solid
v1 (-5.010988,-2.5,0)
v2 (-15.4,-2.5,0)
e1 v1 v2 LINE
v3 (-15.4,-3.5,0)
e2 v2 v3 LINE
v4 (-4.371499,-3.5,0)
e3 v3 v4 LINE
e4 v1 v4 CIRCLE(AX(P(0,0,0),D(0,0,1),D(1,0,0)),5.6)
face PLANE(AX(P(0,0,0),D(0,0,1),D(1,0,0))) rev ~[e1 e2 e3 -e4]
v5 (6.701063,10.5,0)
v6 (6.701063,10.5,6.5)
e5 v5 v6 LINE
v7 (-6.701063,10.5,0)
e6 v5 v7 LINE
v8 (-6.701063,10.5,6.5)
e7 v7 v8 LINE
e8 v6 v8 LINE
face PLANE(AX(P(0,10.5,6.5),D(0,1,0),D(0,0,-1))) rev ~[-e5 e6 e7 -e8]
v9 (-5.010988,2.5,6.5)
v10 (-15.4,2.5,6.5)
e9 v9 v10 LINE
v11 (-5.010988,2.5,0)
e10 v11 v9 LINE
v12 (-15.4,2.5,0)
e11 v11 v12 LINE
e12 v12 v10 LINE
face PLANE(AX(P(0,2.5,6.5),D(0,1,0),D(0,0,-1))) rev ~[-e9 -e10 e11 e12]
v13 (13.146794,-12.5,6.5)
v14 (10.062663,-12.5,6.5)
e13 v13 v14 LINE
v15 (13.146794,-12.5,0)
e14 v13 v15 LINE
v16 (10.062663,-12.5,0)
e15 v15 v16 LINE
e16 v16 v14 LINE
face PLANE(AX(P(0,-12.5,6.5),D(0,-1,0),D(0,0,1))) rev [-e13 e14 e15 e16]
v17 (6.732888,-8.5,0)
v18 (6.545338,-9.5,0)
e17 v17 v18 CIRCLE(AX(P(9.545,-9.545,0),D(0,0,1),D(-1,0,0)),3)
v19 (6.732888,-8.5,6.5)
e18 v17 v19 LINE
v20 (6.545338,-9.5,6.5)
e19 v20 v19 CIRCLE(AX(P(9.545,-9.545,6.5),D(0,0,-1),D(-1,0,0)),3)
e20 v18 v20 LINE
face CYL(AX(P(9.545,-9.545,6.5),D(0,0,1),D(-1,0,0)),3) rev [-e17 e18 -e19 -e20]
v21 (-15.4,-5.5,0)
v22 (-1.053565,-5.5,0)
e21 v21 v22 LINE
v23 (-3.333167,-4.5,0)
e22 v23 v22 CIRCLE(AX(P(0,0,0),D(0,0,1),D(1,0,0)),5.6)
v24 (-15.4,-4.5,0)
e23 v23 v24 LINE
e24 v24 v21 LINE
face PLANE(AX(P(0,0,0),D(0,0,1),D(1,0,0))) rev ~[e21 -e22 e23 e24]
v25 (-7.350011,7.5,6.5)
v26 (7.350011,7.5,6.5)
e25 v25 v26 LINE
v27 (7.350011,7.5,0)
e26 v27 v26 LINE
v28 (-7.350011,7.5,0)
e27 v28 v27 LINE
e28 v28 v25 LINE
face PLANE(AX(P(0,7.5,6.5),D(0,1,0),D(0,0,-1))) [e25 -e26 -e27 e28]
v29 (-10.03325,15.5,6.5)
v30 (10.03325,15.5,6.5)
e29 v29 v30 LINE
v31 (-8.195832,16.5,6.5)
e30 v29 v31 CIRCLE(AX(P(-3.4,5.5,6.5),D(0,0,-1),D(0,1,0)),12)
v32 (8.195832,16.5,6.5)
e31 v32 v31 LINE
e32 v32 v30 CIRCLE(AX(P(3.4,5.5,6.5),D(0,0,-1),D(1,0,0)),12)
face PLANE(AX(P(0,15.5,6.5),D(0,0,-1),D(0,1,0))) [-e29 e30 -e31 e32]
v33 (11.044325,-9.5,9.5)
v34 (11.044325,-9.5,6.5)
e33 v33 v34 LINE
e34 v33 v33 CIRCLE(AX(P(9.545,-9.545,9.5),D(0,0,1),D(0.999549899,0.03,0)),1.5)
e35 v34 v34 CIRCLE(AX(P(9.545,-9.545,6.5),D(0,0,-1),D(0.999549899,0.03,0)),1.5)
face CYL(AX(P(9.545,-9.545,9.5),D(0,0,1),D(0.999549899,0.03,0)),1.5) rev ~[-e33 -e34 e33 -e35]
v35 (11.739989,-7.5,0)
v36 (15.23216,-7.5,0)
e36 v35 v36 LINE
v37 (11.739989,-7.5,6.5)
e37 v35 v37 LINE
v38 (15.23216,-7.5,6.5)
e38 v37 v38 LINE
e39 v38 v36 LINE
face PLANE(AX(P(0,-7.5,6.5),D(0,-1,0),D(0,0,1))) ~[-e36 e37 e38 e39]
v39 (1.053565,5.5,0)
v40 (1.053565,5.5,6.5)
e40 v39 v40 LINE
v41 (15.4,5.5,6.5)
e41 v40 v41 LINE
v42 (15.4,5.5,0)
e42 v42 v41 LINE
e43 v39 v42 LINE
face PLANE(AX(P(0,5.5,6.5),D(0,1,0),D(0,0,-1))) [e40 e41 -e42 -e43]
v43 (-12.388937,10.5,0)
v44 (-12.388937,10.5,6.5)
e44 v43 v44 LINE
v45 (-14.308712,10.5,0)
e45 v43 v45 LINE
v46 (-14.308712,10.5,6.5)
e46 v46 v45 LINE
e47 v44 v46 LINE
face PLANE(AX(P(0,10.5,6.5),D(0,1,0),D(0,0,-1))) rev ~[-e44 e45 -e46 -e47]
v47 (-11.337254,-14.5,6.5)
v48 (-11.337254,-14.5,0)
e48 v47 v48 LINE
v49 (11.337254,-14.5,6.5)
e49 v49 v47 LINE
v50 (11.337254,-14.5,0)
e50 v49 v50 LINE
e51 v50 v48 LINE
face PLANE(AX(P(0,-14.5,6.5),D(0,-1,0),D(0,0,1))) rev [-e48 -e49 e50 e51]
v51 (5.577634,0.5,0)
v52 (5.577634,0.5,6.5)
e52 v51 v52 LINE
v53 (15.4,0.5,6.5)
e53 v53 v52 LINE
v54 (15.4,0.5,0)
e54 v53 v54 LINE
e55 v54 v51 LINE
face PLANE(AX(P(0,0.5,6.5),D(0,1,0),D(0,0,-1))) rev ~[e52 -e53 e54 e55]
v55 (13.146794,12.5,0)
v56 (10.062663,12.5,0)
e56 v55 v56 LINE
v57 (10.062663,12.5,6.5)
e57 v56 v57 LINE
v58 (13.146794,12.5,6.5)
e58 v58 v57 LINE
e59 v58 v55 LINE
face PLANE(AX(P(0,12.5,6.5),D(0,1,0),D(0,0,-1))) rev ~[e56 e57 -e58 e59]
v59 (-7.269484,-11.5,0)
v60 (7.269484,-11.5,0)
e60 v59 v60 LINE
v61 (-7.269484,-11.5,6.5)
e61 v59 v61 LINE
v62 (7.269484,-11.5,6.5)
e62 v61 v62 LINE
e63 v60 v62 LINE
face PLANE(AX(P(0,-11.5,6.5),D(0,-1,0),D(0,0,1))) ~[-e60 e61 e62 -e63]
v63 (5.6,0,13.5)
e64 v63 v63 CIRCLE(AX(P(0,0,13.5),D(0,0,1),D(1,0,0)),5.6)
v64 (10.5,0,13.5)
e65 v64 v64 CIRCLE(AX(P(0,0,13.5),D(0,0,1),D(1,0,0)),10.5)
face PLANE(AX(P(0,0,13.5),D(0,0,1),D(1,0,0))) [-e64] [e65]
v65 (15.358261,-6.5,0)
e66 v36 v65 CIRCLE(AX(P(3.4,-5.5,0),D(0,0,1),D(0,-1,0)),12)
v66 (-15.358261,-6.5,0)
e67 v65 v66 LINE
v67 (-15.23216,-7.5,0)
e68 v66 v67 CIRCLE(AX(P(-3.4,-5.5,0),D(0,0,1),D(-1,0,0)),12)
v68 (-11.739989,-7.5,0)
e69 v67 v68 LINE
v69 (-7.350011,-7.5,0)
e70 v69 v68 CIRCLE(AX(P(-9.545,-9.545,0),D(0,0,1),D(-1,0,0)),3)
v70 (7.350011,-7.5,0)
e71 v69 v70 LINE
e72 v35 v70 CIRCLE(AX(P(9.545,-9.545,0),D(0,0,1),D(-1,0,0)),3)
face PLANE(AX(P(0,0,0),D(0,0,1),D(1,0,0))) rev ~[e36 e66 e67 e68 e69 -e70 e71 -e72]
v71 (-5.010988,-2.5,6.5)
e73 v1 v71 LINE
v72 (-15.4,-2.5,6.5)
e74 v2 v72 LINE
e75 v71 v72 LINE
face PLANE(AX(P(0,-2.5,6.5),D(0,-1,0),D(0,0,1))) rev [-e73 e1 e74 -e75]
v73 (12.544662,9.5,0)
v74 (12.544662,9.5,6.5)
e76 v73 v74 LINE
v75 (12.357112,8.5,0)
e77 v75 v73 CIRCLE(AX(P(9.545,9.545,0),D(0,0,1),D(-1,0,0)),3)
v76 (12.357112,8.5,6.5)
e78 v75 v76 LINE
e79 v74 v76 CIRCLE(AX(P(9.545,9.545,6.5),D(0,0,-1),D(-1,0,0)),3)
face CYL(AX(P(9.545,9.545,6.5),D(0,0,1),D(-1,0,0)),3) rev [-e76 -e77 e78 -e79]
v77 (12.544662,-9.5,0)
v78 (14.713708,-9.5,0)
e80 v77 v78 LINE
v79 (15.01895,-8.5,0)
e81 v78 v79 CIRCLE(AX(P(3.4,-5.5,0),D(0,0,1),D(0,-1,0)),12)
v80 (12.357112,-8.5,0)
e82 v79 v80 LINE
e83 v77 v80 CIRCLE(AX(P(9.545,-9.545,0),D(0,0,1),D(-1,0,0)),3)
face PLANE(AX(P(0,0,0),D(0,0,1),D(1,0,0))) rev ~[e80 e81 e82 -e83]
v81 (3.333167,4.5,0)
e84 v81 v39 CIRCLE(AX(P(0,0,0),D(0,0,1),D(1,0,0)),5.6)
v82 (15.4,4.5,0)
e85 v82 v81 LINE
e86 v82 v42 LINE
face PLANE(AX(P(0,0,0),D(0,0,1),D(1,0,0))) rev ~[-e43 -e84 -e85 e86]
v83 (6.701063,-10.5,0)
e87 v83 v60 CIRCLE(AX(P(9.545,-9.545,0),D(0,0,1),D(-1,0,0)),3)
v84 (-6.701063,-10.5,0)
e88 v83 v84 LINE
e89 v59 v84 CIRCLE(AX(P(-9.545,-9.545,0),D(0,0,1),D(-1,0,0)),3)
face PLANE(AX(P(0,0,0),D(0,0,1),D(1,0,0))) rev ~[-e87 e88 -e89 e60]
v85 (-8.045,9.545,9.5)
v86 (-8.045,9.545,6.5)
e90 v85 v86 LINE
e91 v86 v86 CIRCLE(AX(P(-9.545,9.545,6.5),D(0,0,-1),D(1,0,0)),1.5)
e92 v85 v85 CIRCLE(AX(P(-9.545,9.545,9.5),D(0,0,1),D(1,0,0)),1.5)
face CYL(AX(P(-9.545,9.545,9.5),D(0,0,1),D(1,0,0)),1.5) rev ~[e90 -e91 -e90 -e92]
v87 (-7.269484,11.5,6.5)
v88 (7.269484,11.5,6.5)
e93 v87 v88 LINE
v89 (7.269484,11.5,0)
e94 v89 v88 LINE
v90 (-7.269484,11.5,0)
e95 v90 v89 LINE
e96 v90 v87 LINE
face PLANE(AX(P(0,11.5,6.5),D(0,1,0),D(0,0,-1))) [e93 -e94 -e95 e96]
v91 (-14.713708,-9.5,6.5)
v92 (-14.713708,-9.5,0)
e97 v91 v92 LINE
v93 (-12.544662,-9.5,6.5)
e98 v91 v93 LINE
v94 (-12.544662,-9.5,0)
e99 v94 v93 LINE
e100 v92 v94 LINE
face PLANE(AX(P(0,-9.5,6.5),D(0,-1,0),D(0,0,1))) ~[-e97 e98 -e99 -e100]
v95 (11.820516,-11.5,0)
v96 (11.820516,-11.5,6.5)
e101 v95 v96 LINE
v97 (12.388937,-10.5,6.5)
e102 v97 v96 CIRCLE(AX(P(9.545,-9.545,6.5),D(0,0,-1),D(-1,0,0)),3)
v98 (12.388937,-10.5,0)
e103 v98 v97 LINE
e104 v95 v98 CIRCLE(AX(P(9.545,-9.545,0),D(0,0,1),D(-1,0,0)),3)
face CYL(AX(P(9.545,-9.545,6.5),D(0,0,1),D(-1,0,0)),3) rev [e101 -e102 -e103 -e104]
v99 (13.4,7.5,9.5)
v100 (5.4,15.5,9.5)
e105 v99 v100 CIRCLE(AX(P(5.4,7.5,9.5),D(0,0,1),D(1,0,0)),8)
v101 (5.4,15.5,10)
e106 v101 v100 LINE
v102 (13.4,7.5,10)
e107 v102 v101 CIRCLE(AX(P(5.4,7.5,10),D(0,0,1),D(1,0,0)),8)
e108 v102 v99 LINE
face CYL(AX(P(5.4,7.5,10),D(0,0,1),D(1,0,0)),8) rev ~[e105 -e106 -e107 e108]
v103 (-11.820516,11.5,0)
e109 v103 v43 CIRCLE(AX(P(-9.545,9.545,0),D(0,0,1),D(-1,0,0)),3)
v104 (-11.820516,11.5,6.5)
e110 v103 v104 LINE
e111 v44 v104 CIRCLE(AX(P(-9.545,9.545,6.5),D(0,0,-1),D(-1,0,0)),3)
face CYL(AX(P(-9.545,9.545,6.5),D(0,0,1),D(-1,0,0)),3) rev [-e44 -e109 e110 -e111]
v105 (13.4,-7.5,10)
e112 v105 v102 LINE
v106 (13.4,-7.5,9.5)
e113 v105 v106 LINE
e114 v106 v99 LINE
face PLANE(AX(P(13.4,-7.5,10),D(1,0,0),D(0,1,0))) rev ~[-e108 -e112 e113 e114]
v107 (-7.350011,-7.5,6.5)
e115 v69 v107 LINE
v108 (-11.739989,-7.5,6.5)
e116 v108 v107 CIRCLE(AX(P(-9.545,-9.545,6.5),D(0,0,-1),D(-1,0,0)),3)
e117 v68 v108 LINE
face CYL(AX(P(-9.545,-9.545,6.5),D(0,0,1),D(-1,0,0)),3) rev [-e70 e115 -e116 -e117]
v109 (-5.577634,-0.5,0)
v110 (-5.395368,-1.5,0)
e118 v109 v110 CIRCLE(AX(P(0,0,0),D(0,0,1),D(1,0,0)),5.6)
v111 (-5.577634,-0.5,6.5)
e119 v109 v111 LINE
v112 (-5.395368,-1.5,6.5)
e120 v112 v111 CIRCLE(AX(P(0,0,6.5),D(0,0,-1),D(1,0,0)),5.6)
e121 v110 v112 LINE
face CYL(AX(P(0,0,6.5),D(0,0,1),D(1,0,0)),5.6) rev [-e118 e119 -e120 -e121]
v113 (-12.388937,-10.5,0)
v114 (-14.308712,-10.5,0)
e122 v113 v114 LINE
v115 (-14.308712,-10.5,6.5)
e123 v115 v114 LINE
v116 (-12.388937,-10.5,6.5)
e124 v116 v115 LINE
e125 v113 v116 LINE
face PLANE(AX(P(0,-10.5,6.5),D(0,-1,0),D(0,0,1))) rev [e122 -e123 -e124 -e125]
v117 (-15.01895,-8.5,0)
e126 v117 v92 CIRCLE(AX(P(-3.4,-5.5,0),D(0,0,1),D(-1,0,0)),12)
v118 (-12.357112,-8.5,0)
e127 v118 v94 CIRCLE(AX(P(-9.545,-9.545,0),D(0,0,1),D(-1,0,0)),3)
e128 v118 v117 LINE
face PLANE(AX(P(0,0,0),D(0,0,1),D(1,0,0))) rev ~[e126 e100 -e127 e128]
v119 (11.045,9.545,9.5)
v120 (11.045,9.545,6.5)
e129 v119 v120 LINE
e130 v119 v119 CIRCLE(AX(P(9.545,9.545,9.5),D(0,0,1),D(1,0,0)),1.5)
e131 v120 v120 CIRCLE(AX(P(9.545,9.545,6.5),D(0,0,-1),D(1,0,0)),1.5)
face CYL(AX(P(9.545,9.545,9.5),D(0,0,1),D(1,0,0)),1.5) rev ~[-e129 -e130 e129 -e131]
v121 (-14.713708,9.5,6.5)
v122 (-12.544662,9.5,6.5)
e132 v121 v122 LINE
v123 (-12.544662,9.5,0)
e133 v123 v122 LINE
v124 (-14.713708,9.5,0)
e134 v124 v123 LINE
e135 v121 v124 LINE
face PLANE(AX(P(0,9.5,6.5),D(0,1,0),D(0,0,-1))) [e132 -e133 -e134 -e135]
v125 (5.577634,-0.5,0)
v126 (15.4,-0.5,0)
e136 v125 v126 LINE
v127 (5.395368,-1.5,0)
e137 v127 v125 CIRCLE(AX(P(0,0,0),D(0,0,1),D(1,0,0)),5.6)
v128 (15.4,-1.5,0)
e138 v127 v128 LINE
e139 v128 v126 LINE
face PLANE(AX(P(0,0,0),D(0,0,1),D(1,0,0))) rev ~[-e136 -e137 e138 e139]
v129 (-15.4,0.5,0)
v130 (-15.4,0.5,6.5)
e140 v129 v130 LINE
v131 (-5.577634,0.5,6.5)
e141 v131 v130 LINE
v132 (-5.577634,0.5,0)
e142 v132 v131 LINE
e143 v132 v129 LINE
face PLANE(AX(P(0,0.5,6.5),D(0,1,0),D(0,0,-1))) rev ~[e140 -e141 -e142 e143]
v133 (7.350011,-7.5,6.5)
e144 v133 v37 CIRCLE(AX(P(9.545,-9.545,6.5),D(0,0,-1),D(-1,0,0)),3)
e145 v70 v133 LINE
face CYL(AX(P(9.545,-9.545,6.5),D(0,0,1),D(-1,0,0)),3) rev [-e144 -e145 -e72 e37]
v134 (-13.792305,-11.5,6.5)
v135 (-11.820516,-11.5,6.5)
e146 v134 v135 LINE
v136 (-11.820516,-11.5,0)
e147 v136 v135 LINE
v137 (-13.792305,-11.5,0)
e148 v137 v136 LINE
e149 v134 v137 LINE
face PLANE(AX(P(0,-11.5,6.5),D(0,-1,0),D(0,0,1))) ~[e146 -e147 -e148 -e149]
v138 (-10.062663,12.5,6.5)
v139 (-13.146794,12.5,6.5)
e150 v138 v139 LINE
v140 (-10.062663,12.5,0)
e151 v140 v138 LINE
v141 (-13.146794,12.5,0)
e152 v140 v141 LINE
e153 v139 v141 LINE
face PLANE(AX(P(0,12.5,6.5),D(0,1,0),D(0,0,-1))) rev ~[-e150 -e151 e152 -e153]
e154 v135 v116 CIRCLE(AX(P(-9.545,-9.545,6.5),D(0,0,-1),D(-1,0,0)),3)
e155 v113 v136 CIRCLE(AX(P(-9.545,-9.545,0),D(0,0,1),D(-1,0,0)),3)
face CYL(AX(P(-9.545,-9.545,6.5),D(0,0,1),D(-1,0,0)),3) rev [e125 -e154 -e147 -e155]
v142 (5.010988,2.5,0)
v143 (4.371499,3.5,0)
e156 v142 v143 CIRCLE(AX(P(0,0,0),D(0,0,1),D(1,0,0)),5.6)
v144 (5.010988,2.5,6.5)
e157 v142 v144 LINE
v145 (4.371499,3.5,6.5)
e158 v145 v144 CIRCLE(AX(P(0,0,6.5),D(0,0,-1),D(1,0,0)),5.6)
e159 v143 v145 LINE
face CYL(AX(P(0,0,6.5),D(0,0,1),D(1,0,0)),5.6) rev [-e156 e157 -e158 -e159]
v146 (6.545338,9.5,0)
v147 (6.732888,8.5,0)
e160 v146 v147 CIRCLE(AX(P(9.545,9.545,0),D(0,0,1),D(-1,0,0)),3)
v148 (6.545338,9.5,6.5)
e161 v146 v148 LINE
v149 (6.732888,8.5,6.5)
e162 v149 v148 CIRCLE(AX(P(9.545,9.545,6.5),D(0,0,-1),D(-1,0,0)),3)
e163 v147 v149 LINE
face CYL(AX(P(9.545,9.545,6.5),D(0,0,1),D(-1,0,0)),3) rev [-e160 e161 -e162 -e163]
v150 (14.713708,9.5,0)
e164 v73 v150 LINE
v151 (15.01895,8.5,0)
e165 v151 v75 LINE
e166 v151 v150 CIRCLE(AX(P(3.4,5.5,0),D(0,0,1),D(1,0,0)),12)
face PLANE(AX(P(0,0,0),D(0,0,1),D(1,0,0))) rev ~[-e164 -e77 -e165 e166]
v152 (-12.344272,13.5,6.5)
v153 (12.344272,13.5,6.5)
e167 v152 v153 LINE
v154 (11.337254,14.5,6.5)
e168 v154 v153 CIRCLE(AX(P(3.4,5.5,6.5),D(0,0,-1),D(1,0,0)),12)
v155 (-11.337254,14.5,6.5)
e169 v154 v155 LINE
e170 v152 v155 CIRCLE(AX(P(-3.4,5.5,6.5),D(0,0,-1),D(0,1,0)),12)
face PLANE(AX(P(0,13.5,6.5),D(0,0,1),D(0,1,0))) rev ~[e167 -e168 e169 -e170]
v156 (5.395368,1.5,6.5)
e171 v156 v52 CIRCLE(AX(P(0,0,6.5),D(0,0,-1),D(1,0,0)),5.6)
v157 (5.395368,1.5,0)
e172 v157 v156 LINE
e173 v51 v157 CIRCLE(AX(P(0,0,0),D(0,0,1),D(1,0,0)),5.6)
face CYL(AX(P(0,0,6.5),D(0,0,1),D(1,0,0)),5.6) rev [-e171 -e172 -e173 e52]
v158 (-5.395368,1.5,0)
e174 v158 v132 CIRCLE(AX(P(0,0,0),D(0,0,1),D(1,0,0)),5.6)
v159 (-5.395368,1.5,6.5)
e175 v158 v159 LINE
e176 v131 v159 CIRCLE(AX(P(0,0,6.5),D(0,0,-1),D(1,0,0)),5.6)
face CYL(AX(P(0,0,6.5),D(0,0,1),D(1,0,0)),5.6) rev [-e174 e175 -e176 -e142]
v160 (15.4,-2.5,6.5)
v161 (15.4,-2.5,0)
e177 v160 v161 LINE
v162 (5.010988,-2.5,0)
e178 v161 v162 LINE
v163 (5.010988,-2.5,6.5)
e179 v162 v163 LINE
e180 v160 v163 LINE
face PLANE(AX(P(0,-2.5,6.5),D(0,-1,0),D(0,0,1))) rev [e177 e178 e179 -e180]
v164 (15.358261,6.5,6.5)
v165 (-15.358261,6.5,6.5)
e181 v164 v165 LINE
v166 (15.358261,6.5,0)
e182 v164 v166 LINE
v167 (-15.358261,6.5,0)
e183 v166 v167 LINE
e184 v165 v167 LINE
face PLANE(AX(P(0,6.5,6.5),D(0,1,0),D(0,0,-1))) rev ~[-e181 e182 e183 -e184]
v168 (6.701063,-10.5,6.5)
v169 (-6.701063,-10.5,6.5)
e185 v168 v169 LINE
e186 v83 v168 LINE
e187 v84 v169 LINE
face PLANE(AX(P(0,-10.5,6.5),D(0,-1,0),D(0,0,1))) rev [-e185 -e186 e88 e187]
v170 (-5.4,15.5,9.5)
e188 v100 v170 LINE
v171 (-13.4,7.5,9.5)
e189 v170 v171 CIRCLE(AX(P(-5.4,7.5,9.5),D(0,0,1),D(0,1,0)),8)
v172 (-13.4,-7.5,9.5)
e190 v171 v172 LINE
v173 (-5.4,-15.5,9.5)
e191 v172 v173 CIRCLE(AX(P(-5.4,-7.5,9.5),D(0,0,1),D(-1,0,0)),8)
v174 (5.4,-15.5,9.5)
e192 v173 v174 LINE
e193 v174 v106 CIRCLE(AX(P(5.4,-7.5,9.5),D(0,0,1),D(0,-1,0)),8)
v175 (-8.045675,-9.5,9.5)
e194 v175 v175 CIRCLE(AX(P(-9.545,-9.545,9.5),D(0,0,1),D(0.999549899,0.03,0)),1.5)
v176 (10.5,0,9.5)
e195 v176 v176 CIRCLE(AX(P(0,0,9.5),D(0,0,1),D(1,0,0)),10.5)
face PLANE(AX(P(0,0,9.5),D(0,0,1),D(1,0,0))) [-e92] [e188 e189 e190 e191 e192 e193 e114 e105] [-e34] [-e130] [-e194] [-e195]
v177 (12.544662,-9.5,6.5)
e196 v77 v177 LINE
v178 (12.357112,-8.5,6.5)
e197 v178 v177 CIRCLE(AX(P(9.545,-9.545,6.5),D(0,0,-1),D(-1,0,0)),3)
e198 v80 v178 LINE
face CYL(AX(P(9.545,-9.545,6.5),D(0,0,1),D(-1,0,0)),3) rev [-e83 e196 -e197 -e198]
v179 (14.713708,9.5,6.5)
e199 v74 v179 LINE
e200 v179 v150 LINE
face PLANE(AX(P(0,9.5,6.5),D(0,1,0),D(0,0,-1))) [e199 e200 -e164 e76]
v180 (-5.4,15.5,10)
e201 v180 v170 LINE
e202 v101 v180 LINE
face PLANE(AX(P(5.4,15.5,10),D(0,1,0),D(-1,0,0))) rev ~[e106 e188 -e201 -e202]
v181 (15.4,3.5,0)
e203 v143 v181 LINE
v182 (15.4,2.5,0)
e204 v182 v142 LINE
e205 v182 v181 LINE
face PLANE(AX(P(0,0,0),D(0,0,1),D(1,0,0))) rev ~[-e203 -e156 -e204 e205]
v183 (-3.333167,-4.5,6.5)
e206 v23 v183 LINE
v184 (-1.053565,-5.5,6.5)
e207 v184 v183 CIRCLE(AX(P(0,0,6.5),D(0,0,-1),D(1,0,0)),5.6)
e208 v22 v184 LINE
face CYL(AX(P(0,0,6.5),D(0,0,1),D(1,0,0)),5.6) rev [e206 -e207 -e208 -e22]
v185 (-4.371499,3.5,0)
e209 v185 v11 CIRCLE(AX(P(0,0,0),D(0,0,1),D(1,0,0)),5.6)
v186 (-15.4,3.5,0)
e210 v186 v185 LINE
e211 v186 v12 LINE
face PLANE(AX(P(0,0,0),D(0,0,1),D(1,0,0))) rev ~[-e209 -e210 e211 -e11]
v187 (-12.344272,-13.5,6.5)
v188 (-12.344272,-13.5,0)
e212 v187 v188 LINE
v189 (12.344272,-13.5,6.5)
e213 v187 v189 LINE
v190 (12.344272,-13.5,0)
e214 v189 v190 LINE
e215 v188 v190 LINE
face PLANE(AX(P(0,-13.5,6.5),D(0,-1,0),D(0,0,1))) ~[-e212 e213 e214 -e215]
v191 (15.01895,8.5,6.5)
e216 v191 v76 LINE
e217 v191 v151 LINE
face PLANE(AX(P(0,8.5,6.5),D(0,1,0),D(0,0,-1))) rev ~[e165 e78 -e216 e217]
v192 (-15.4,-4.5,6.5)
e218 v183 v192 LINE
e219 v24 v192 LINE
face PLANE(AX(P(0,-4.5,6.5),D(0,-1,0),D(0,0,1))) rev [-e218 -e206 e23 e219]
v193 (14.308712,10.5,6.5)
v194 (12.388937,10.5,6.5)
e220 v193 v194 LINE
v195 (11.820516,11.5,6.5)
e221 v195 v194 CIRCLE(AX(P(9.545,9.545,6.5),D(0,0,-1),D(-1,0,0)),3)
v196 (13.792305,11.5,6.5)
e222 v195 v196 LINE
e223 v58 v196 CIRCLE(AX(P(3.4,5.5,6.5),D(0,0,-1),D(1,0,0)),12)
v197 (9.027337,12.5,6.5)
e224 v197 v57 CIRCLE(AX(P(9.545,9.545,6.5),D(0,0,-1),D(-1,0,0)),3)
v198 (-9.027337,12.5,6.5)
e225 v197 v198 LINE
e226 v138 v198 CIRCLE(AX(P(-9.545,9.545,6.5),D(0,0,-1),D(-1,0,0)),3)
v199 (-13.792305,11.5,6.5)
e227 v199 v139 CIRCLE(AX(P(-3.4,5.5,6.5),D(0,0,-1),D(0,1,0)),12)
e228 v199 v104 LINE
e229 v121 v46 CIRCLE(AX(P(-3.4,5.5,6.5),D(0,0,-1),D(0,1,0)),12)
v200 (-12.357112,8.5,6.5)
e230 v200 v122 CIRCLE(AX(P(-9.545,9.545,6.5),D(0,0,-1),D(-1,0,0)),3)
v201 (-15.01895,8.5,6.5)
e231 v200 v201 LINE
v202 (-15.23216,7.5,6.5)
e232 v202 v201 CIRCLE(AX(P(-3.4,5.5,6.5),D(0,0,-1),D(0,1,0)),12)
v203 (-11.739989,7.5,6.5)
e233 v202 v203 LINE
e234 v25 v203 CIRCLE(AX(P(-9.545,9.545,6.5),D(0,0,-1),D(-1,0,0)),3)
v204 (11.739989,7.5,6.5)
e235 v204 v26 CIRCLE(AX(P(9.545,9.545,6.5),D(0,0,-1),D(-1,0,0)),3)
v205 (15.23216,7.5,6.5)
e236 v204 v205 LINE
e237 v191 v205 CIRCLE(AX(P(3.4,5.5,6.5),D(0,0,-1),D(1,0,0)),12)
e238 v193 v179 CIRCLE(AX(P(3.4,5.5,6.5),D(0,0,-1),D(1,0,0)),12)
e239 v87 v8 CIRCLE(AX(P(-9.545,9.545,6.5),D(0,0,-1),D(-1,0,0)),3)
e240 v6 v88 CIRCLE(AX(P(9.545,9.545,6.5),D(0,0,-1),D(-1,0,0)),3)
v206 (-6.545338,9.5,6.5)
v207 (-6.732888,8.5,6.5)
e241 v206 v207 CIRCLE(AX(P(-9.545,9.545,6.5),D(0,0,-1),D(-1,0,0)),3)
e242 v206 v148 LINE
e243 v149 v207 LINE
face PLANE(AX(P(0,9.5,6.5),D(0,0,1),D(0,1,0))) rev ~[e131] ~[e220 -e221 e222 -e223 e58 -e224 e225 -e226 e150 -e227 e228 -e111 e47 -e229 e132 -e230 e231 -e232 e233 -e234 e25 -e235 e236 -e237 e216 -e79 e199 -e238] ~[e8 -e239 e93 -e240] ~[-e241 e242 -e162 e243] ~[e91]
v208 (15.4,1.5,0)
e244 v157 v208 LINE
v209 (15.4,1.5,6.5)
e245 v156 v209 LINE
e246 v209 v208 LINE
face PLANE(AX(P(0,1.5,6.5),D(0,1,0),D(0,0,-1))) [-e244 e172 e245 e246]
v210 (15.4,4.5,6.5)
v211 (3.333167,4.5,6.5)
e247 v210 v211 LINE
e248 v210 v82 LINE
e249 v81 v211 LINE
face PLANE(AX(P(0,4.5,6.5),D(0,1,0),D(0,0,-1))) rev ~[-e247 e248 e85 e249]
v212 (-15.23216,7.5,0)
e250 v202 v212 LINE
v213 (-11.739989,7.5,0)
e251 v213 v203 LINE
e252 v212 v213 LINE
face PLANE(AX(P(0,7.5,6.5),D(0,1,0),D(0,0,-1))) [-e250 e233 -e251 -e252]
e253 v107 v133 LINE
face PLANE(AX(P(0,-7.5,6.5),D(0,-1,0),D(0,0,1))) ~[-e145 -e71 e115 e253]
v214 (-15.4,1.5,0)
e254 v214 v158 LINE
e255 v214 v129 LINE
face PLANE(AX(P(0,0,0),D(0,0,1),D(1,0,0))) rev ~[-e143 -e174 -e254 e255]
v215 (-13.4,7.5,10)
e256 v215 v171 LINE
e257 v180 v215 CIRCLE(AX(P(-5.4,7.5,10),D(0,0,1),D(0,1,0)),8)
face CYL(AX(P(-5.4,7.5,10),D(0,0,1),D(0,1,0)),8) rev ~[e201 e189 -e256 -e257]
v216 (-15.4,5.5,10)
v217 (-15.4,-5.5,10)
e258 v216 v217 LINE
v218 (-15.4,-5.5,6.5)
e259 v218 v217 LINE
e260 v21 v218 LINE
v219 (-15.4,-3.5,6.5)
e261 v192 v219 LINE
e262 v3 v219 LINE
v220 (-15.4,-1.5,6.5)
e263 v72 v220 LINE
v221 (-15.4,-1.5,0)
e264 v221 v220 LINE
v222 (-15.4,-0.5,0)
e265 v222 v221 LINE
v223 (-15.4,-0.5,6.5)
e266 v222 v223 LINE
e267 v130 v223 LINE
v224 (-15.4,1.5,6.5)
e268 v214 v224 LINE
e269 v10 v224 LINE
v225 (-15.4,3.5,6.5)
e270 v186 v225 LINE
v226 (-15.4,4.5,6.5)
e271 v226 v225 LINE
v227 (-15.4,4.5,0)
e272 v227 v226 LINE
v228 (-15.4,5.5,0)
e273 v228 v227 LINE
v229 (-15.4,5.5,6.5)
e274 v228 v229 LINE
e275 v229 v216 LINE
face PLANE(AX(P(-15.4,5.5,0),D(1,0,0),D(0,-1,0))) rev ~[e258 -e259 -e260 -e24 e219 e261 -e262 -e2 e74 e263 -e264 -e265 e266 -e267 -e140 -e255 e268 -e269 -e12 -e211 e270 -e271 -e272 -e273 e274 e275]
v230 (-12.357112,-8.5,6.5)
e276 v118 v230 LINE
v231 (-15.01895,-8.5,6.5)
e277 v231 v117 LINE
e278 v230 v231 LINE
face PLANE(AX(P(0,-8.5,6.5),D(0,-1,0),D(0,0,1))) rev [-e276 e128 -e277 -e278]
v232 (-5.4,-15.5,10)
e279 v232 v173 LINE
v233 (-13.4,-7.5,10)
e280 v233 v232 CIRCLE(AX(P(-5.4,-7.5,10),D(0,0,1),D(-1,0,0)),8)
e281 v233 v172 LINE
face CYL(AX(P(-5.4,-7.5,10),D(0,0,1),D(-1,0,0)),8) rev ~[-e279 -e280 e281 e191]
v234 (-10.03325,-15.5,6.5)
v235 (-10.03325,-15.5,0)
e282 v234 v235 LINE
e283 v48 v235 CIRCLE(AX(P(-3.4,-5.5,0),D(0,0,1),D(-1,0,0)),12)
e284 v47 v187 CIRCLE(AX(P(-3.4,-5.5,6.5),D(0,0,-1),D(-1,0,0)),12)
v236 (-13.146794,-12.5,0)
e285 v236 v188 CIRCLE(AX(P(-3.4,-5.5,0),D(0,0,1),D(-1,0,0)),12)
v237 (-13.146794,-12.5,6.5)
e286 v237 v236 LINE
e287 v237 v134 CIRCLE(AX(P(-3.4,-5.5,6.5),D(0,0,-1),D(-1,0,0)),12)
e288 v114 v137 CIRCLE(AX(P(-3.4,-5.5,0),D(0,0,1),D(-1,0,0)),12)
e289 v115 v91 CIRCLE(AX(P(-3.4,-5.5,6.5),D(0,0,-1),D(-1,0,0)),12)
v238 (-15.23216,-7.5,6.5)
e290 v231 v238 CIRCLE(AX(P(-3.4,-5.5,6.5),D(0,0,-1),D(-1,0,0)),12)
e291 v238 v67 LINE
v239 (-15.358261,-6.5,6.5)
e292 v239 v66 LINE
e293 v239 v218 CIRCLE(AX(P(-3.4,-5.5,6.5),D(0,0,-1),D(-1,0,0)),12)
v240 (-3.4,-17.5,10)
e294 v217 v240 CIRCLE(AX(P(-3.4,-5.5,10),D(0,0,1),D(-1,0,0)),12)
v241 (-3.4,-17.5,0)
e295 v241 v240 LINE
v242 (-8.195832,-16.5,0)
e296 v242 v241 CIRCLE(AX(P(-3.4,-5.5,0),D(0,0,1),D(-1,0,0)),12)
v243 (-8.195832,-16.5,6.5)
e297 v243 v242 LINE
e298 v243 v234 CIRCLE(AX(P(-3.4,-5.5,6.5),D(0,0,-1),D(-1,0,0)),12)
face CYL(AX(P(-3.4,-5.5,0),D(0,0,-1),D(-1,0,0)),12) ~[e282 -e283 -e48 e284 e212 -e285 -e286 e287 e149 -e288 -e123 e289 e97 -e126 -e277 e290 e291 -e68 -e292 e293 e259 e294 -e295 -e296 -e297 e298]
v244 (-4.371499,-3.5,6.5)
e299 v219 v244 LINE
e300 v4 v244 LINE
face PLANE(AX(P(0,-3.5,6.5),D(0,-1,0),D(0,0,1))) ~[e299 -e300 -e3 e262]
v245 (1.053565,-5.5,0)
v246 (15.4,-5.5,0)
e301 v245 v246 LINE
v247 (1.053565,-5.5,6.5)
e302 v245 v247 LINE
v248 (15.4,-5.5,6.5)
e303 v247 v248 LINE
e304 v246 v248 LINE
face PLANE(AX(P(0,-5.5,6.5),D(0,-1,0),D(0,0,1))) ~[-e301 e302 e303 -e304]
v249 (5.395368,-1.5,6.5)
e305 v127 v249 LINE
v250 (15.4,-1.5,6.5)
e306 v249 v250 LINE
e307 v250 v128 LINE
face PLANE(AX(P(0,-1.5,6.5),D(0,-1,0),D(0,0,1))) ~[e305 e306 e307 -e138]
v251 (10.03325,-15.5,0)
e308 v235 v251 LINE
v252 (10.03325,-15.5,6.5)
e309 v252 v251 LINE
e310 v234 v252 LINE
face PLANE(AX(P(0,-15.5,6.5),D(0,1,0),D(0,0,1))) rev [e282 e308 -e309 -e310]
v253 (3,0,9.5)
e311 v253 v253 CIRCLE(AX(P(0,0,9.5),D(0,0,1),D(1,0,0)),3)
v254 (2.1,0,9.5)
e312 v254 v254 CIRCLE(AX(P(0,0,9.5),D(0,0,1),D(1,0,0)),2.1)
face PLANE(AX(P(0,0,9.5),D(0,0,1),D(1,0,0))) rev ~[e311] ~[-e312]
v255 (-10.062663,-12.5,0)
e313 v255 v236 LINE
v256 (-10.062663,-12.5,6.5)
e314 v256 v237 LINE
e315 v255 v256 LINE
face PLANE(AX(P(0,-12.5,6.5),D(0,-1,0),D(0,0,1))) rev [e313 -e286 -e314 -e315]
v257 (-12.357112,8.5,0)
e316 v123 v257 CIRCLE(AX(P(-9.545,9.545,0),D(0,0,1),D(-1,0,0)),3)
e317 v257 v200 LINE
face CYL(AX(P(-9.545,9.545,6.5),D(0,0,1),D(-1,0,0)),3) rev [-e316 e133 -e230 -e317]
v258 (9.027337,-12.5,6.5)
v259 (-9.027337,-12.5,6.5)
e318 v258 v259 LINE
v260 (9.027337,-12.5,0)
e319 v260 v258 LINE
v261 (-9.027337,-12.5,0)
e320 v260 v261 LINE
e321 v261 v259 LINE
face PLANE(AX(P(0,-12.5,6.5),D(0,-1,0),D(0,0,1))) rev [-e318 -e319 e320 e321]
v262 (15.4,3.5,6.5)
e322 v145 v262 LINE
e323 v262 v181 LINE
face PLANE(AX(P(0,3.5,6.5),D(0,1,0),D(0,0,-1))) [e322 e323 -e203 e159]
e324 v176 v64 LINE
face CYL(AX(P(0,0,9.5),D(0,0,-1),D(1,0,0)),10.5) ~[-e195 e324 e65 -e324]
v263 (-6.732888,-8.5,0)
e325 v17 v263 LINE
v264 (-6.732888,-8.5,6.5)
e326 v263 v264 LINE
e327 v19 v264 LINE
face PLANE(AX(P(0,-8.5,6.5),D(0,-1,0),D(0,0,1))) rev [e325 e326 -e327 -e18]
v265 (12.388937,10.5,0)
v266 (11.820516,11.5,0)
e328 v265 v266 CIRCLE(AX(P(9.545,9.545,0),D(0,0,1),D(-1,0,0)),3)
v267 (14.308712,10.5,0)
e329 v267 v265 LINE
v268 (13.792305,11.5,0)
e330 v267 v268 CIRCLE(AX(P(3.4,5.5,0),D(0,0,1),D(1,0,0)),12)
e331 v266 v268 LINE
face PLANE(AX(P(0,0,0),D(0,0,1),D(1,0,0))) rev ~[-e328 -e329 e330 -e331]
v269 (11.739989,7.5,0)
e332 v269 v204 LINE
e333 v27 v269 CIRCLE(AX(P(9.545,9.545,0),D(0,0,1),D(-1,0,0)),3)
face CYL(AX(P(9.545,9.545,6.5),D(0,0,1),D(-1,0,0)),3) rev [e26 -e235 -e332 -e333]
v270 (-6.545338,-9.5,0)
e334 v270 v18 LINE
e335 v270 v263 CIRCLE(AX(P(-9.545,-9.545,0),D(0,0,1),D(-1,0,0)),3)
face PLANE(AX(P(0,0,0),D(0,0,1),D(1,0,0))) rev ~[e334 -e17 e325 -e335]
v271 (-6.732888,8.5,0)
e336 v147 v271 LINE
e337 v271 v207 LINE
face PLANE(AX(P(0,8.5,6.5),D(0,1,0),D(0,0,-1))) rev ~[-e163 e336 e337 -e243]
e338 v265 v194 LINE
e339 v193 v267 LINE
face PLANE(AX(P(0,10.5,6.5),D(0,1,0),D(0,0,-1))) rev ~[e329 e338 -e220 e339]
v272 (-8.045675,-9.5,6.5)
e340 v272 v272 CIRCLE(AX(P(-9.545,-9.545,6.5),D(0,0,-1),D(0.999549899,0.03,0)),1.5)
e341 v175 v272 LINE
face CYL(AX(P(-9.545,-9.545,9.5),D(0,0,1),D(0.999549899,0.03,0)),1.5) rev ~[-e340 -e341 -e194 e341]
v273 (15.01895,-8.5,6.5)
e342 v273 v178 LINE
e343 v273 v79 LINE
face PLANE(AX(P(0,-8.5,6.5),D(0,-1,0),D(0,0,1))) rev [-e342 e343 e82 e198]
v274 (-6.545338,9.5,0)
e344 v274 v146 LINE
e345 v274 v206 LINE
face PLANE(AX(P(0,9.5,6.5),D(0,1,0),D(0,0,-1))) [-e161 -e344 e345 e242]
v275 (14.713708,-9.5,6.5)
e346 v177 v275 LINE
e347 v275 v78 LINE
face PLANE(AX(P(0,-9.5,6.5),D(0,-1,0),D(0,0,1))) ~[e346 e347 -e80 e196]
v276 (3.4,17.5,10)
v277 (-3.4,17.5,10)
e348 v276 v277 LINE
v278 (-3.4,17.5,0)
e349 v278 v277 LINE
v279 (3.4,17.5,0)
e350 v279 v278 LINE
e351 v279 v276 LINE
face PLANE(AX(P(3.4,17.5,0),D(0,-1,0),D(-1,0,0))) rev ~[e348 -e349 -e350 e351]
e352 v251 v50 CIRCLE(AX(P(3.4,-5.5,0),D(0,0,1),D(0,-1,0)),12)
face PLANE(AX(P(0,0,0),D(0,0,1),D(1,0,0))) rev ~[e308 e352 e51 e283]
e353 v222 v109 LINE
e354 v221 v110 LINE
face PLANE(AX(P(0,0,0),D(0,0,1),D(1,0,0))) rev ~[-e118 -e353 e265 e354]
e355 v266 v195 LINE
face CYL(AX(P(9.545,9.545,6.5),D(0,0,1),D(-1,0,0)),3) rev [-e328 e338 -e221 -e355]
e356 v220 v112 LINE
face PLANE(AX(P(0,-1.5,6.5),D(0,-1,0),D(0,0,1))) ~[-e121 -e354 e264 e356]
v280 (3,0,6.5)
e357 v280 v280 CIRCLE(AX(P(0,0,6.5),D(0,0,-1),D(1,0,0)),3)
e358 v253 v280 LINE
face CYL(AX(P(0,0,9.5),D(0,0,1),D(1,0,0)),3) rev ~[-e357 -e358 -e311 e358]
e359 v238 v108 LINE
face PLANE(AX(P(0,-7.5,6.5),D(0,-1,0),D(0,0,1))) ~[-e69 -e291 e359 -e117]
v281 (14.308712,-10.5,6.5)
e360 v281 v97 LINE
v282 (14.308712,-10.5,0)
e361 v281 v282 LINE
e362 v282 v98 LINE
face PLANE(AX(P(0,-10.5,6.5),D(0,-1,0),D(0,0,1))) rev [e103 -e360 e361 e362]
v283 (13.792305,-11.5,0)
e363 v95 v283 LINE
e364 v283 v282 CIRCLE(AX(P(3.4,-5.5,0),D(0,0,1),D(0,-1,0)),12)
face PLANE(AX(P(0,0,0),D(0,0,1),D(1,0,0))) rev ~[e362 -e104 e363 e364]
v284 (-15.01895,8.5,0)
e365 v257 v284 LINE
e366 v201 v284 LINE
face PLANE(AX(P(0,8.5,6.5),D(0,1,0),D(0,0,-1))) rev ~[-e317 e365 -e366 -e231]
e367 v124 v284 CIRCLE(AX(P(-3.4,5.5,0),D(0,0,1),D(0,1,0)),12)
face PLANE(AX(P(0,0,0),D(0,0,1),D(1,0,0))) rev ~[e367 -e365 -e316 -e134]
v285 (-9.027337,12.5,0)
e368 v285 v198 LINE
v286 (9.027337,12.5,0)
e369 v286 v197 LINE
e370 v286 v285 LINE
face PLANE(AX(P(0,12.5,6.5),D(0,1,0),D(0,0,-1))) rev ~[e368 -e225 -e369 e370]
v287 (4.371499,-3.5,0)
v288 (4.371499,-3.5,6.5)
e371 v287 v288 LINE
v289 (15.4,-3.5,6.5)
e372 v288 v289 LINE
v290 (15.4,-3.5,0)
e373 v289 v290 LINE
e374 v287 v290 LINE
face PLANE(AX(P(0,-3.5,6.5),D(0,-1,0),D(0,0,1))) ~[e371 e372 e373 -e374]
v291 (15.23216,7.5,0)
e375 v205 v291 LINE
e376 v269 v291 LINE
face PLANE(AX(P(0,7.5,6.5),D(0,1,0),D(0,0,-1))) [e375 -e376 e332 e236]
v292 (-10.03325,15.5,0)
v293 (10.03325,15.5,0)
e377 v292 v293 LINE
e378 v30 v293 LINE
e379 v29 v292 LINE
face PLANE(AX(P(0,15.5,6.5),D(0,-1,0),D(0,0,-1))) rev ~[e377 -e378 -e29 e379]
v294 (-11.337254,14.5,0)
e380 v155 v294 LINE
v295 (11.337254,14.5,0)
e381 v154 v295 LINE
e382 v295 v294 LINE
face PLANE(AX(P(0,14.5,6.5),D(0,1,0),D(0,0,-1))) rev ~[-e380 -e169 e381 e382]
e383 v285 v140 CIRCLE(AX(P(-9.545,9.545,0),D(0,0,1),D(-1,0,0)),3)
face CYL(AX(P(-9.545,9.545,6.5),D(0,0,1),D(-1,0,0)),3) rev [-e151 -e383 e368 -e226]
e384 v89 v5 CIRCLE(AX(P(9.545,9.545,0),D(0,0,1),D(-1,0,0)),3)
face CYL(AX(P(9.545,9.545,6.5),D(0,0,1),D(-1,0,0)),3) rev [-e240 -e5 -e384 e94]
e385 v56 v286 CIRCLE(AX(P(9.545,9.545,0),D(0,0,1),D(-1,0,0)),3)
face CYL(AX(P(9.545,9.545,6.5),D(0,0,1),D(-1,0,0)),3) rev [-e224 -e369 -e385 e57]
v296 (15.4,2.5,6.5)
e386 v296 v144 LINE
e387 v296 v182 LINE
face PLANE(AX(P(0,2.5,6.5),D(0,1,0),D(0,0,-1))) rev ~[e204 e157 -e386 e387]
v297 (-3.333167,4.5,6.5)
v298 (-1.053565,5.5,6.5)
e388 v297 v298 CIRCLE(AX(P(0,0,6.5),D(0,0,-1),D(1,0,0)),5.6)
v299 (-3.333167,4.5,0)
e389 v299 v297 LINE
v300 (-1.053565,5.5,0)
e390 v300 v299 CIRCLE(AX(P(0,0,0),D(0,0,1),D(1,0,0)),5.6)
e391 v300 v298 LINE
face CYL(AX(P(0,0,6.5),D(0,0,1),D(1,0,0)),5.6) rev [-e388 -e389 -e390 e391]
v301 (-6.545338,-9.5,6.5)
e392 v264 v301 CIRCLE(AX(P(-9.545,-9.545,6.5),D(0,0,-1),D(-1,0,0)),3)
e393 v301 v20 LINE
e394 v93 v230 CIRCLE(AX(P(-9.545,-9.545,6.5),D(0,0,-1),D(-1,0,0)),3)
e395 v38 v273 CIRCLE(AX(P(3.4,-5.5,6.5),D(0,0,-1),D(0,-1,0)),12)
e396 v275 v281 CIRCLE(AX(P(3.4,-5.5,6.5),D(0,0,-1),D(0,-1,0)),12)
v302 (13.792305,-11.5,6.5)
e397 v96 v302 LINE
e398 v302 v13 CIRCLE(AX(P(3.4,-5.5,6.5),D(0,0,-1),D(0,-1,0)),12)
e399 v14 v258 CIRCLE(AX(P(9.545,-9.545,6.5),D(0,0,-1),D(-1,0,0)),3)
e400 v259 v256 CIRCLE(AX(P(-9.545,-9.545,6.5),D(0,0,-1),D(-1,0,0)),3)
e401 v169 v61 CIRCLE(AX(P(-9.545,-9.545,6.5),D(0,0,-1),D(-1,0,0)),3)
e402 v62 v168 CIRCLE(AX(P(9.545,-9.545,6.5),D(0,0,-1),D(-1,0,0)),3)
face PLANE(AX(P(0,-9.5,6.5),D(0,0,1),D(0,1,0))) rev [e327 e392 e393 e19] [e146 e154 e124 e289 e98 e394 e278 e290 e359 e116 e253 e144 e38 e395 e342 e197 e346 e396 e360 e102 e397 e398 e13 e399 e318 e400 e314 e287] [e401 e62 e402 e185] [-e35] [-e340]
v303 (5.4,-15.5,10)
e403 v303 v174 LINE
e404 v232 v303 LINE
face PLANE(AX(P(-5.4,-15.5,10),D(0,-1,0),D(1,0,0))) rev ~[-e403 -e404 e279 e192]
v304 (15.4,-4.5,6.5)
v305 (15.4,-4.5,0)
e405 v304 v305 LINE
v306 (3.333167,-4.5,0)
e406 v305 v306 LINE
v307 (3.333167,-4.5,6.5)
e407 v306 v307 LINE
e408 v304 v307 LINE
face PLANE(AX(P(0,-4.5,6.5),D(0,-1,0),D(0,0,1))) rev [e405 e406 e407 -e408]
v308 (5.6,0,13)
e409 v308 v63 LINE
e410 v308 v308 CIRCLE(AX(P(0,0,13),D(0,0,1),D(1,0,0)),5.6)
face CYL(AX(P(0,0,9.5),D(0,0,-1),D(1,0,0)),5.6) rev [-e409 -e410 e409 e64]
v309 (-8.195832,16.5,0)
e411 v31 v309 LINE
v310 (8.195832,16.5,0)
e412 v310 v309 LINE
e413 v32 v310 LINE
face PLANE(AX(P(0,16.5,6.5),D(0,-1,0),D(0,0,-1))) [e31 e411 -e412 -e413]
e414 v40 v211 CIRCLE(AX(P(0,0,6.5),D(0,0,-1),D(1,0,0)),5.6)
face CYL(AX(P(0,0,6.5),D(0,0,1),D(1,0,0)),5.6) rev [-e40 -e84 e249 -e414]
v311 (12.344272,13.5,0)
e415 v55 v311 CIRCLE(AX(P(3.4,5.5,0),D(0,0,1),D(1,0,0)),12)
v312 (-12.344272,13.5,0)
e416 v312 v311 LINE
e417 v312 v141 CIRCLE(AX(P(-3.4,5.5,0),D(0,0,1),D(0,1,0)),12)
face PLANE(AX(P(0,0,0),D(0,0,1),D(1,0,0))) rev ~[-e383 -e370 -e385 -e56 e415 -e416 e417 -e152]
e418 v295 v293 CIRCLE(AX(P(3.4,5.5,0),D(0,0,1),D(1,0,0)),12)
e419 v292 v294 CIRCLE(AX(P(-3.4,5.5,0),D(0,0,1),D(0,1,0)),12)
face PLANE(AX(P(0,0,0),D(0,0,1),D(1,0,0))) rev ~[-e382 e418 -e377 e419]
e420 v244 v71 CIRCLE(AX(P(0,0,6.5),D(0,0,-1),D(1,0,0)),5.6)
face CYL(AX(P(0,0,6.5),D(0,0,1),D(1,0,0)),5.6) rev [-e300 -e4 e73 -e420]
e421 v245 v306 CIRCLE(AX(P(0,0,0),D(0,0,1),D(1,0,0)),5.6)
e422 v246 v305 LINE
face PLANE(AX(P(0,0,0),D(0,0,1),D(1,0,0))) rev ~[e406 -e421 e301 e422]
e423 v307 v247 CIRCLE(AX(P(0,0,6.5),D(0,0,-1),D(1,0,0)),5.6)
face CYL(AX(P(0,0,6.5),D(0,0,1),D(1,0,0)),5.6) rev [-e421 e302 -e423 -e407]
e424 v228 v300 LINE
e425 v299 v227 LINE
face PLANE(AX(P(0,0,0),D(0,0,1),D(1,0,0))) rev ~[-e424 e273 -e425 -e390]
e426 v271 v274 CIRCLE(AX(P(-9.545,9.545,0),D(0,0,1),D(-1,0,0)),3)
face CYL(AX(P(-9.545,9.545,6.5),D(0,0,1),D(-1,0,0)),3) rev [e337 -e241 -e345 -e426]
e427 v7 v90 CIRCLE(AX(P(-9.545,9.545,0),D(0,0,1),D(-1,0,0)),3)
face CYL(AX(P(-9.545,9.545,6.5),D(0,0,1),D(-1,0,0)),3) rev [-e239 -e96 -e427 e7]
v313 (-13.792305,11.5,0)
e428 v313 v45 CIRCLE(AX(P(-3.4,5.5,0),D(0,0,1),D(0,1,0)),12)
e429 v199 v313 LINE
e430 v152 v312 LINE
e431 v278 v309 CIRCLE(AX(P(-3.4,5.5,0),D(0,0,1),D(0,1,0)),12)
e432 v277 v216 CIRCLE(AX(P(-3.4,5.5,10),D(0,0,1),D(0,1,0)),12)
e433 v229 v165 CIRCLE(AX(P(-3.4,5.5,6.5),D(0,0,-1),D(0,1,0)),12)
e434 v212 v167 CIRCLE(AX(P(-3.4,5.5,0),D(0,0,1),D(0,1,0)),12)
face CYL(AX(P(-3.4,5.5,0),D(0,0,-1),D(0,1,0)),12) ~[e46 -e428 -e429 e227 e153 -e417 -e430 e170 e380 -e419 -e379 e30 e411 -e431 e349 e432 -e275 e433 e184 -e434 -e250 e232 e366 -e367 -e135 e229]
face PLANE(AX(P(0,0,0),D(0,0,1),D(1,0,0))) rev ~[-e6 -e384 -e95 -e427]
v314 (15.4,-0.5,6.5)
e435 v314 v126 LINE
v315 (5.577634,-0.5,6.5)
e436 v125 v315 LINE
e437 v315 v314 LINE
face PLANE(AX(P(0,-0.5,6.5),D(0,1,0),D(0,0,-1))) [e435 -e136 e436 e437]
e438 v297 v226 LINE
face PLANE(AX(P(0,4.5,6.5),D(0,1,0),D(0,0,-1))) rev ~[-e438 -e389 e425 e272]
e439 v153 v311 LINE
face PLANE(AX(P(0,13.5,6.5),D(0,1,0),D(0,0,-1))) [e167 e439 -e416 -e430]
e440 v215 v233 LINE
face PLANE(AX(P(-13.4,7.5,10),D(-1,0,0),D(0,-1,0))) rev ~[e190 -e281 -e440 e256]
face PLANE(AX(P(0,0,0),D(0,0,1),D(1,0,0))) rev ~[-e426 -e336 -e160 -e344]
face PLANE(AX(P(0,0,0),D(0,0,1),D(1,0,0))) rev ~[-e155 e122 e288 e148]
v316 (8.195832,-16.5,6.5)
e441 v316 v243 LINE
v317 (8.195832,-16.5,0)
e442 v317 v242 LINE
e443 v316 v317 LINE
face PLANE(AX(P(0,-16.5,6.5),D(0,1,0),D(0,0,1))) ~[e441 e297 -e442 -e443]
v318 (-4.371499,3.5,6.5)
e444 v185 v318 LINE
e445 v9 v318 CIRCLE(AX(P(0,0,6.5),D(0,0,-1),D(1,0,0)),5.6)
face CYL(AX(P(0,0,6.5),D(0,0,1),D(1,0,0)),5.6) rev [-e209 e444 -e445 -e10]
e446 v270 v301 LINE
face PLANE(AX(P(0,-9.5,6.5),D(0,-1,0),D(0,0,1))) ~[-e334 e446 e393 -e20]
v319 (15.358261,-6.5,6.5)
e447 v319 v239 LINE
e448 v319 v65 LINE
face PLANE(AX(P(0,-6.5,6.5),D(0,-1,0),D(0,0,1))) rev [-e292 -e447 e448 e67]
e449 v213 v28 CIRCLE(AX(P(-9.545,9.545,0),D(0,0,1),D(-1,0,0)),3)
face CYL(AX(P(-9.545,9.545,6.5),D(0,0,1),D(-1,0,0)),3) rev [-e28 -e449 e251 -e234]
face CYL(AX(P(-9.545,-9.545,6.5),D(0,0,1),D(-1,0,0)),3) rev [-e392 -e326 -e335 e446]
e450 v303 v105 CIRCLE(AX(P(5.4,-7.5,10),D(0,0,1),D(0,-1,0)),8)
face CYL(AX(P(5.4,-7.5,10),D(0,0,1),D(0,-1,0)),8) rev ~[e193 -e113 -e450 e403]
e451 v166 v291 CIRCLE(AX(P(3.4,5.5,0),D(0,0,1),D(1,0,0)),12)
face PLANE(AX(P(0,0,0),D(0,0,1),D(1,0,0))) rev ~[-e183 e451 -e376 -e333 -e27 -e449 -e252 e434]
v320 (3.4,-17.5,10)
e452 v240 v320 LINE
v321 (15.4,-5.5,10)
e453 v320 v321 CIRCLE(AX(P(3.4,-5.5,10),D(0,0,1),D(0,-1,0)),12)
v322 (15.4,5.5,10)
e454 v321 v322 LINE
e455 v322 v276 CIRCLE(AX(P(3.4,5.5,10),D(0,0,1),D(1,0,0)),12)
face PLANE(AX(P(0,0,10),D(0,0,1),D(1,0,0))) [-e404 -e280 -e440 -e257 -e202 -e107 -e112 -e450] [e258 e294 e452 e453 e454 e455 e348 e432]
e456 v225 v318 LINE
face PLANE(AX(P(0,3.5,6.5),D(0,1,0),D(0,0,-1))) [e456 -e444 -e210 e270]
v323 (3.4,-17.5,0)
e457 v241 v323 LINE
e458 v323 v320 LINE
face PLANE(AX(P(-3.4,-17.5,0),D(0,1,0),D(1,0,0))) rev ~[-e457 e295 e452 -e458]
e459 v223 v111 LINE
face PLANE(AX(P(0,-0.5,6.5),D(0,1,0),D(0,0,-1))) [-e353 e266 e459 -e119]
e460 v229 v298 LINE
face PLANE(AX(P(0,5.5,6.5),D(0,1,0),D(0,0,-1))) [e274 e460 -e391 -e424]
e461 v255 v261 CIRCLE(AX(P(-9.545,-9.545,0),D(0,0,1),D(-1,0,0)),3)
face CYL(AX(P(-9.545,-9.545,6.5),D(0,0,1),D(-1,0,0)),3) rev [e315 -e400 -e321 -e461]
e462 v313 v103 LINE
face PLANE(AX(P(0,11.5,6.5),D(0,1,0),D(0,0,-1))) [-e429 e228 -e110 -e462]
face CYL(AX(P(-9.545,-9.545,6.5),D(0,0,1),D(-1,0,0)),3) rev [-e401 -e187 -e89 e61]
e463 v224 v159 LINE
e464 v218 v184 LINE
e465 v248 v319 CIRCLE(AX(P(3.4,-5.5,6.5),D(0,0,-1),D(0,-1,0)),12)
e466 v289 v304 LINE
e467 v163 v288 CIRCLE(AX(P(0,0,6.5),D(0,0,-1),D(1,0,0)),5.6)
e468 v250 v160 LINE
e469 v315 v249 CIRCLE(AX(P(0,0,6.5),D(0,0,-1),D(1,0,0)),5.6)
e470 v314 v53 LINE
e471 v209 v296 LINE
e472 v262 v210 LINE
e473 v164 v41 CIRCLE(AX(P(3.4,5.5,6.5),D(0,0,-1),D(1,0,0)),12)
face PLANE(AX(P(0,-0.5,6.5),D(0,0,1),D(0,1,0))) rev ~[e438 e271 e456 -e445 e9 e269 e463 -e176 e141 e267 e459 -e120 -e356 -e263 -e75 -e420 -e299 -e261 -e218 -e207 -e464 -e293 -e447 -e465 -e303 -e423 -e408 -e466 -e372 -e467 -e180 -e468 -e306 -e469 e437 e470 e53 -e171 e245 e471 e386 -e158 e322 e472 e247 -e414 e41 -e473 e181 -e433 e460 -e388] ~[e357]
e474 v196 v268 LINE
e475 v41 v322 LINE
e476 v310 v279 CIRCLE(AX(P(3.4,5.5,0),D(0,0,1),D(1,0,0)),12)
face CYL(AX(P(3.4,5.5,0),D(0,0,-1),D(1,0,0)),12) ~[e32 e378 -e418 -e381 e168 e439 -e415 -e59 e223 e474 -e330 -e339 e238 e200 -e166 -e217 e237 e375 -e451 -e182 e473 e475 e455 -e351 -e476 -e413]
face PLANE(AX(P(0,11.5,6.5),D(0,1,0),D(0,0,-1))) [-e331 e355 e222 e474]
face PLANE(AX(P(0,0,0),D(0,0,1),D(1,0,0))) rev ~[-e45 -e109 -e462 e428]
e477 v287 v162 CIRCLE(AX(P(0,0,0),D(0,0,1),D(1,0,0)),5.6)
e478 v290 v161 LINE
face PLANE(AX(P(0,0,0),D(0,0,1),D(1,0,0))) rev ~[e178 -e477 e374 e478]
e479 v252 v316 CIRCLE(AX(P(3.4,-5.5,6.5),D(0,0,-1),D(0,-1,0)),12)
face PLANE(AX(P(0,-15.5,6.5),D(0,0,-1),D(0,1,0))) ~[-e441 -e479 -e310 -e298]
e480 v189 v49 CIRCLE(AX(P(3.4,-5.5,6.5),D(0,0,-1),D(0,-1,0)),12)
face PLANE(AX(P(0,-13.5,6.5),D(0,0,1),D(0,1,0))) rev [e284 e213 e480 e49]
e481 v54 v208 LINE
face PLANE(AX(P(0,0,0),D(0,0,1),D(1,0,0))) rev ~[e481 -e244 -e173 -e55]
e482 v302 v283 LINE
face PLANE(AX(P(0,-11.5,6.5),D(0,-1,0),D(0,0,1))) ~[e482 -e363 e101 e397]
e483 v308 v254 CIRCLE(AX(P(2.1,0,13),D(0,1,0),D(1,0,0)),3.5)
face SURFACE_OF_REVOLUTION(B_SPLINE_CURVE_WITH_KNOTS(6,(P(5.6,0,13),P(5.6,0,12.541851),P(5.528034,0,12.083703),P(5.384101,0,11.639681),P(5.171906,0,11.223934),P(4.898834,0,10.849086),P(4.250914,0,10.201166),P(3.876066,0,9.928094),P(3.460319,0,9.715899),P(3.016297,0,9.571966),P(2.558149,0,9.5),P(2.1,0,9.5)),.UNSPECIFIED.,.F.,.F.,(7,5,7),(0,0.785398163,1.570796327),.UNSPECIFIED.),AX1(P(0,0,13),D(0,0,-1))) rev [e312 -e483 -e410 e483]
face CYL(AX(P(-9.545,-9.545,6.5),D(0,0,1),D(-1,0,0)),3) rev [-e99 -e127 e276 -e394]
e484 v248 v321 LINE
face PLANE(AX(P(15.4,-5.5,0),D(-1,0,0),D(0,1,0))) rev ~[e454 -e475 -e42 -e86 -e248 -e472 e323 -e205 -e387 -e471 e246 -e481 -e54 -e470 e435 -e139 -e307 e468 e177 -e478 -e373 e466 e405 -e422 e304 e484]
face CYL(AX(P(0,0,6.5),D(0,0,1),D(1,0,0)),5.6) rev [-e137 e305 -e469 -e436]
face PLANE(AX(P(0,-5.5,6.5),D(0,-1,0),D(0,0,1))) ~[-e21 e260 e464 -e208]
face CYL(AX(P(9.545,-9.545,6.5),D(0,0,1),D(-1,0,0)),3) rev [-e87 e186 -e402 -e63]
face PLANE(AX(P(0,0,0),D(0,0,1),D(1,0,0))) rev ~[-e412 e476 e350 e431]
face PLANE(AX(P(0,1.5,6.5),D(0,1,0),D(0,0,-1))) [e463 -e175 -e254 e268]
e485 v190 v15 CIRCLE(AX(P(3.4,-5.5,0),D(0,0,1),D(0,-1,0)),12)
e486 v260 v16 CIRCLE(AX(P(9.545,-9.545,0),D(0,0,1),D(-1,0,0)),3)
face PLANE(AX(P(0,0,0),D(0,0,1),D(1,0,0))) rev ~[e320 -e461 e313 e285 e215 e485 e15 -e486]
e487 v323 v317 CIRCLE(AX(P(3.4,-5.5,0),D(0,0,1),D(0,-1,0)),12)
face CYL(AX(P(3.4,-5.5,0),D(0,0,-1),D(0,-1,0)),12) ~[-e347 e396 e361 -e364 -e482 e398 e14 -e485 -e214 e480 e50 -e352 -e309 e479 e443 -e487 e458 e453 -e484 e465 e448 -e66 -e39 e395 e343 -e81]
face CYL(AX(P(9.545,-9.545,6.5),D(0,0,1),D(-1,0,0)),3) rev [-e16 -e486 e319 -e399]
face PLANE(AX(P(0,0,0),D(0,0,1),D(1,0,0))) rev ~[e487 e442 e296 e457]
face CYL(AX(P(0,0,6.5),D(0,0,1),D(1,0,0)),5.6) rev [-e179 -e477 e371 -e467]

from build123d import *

# Parameters (mm, degrees)
HEAD_BASE_BODY_DEPTH       = 10
FACE_RECESS_0_5MM_DEPTH    = 0.5
HUB_SKETCH_R               = 10.5
HUB_SKETCH_R_2             = 5.6
RAISED_HUB_21_DEPTH        = 4
RECESS_FILLET_R3_5_R       = 3.5
CENTRE_BORE_SKETCH_R       = 3
CENTRE_BORE_6_DEPTH        = 3.5
COOLING_FIN_SLOTS_SKETCH_W = 6.5
COOLING_FIN_SLOTS_SKETCH_H = 1
COOLING_FIN_SLOTS_DEPTH    = 27.93807714
MOUNTING_HOLES_SKETCH_R    = 1.5
MOUNTING_HOLES_3_DEPTH     = 3.5
HUB_BORE_SKETCH_R          = 5.6
HUB_BORE_11_2_DEPTH        = 25.339474111
SIDE_CUT_SKETCH_R          = 3
SIDE_CUT_6X6_DEPTH         = 25.339474111


with BuildPart() as part:
    # Head Outline Sketch → Head Base Body (new body)
    with BuildSketch(Plane.XY):
        with BuildLine():
            Line((-3.4, -17.5), (3.4, -17.5))
            ThreePointArc((3.4, -17.5), (11.885281374, -13.985281374), (15.4, -5.5))
            Line((15.4, -5.5), (15.4, 5.5))
            ThreePointArc((15.4, 5.5), (11.885281374, 13.985281374), (3.4, 17.5))
            Line((3.4, 17.5), (-3.4, 17.5))
            ThreePointArc((-3.4, 17.5), (-11.885281374, 13.985281374), (-15.4, 5.5))
            Line((-15.4, 5.5), (-15.4, -5.5))
            ThreePointArc((-15.4, -5.5), (-11.885281374, -13.985281374), (-3.4, -17.5))
        make_face()
    extrude(amount=HEAD_BASE_BODY_DEPTH)

    # Face Recess Sketch → Face Recess 0.5mm (cut)
    with BuildSketch(Plane.XY.offset(10)):
        with BuildLine():
            Line((-13.4, 7.5), (-13.4, -7.5))
            ThreePointArc((-13.4, -7.5), (-11.056854249, -13.156854249), (-5.4, -15.5))
            Line((-5.4, -15.5), (5.4, -15.5))
            ThreePointArc((5.4, -15.5), (11.056854249, -13.156854249), (13.4, -7.5))
            Line((13.4, -7.5), (13.4, 7.5))
            ThreePointArc((13.4, 7.5), (11.056854249, 13.156854249), (5.4, 15.5))
            Line((5.4, 15.5), (-5.4, 15.5))
            ThreePointArc((-5.4, 15.5), (-11.056854249, 13.156854249), (-13.4, 7.5))
        make_face()
    extrude(amount=-FACE_RECESS_0_5MM_DEPTH, mode=Mode.SUBTRACT)

    # Hub Sketch → Raised Hub Ø21 (add)
    with BuildSketch(Plane.XY.offset(9.5)):
        Circle(HUB_SKETCH_R)
        Circle(HUB_SKETCH_R_2, mode=Mode.SUBTRACT)
    extrude(amount=RAISED_HUB_21_DEPTH)

    # Recess Fillet R3.5
    recess_fillet_r3_5_edges = [part.edges().sort_by_distance(p)[0] for p in [
        (-5.6, 0, 9.5),
    ]]
    fillet(recess_fillet_r3_5_edges, radius=RECESS_FILLET_R3_5_R)

    # Centre Bore Sketch → Centre Bore Ø6 (cut)
    with BuildSketch(Plane.XY.offset(9.5)):
        Circle(CENTRE_BORE_SKETCH_R)
    extrude(amount=-CENTRE_BORE_6_DEPTH, mode=Mode.SUBTRACT)

    # Cooling Fin Slots Sketch → Cooling Fin Slots (cut, symmetric)
    with BuildSketch(Plane(origin=(0, 0, 0), x_dir=(0, 0, -1), z_dir=(1, 0, 0))):
        with Locations((-3.25, 2)):
            Rectangle(COOLING_FIN_SLOTS_SKETCH_W, COOLING_FIN_SLOTS_SKETCH_H)
        with Locations((-3.25, 0)):
            Rectangle(COOLING_FIN_SLOTS_SKETCH_W, COOLING_FIN_SLOTS_SKETCH_H)
        with Locations((-3.25, 4)):
            Rectangle(COOLING_FIN_SLOTS_SKETCH_W, COOLING_FIN_SLOTS_SKETCH_H)
        with Locations((-3.25, 6)):
            Rectangle(COOLING_FIN_SLOTS_SKETCH_W, COOLING_FIN_SLOTS_SKETCH_H)
        with Locations((-3.25, 8)):
            Rectangle(COOLING_FIN_SLOTS_SKETCH_W, COOLING_FIN_SLOTS_SKETCH_H)
        with Locations((-3.25, 10)):
            Rectangle(COOLING_FIN_SLOTS_SKETCH_W, COOLING_FIN_SLOTS_SKETCH_H)
        with Locations((-3.25, 12)):
            Rectangle(COOLING_FIN_SLOTS_SKETCH_W, COOLING_FIN_SLOTS_SKETCH_H)
        with Locations((-3.25, 14)):
            Rectangle(COOLING_FIN_SLOTS_SKETCH_W, COOLING_FIN_SLOTS_SKETCH_H)
        with Locations((-3.25, 16)):
            Rectangle(COOLING_FIN_SLOTS_SKETCH_W, COOLING_FIN_SLOTS_SKETCH_H)
    cooling_fin_slots = extrude(amount=COOLING_FIN_SLOTS_DEPTH, both=True, mode=Mode.SUBTRACT)

    # Cooling Fin Slots Mirror: Cooling Fin Slots across plane
    add(cooling_fin_slots.mirror(Plane.ZX), mode=Mode.SUBTRACT)

    # Mounting Holes Sketch → Mounting Holes Ø3 (cut)
    with BuildSketch(Plane.XY.offset(9.5)):
        with Locations((-9.545, 9.545)):
            Circle(MOUNTING_HOLES_SKETCH_R)
        with Locations((9.545, 9.545)):
            Circle(MOUNTING_HOLES_SKETCH_R)
        with Locations(Location((9.545, -9.545, 0), (0, 0, 1.719131321))):
            Circle(MOUNTING_HOLES_SKETCH_R)
        with Locations(Location((-9.545, -9.545, 0), (0, 0, 1.719131321))):
            Circle(MOUNTING_HOLES_SKETCH_R)
    extrude(amount=-MOUNTING_HOLES_3_DEPTH, mode=Mode.SUBTRACT)

    # Hub Bore Sketch → Hub Bore Ø11.2 (cut, through all)
    with BuildSketch(Plane(origin=(0, 0, 6.5), x_dir=(-1, 0, 0), z_dir=(0, 0, -1))):
        with Locations(Location((0, 0, 0), (0, 0, 180))):
            Circle(HUB_BORE_SKETCH_R)
    extrude(amount=HUB_BORE_11_2_DEPTH, mode=Mode.SUBTRACT)

    # Side Cut Sketch → Side Cut 6x6 (cut, through all)
    with BuildSketch(Plane(origin=(0, 0, 6.5), x_dir=(-1, 0, 0), z_dir=(0, 0, -1))):
        with Locations((-9.545, 9.545)):
            Circle(SIDE_CUT_SKETCH_R)
        with Locations((9.545, 9.545)):
            Circle(SIDE_CUT_SKETCH_R)
        with Locations((-9.545, -9.545)):
            Circle(SIDE_CUT_SKETCH_R)
        with Locations((9.545, -9.545)):
            Circle(SIDE_CUT_SKETCH_R)
    extrude(amount=SIDE_CUT_6X6_DEPTH, mode=Mode.SUBTRACT)


solid = part.part
